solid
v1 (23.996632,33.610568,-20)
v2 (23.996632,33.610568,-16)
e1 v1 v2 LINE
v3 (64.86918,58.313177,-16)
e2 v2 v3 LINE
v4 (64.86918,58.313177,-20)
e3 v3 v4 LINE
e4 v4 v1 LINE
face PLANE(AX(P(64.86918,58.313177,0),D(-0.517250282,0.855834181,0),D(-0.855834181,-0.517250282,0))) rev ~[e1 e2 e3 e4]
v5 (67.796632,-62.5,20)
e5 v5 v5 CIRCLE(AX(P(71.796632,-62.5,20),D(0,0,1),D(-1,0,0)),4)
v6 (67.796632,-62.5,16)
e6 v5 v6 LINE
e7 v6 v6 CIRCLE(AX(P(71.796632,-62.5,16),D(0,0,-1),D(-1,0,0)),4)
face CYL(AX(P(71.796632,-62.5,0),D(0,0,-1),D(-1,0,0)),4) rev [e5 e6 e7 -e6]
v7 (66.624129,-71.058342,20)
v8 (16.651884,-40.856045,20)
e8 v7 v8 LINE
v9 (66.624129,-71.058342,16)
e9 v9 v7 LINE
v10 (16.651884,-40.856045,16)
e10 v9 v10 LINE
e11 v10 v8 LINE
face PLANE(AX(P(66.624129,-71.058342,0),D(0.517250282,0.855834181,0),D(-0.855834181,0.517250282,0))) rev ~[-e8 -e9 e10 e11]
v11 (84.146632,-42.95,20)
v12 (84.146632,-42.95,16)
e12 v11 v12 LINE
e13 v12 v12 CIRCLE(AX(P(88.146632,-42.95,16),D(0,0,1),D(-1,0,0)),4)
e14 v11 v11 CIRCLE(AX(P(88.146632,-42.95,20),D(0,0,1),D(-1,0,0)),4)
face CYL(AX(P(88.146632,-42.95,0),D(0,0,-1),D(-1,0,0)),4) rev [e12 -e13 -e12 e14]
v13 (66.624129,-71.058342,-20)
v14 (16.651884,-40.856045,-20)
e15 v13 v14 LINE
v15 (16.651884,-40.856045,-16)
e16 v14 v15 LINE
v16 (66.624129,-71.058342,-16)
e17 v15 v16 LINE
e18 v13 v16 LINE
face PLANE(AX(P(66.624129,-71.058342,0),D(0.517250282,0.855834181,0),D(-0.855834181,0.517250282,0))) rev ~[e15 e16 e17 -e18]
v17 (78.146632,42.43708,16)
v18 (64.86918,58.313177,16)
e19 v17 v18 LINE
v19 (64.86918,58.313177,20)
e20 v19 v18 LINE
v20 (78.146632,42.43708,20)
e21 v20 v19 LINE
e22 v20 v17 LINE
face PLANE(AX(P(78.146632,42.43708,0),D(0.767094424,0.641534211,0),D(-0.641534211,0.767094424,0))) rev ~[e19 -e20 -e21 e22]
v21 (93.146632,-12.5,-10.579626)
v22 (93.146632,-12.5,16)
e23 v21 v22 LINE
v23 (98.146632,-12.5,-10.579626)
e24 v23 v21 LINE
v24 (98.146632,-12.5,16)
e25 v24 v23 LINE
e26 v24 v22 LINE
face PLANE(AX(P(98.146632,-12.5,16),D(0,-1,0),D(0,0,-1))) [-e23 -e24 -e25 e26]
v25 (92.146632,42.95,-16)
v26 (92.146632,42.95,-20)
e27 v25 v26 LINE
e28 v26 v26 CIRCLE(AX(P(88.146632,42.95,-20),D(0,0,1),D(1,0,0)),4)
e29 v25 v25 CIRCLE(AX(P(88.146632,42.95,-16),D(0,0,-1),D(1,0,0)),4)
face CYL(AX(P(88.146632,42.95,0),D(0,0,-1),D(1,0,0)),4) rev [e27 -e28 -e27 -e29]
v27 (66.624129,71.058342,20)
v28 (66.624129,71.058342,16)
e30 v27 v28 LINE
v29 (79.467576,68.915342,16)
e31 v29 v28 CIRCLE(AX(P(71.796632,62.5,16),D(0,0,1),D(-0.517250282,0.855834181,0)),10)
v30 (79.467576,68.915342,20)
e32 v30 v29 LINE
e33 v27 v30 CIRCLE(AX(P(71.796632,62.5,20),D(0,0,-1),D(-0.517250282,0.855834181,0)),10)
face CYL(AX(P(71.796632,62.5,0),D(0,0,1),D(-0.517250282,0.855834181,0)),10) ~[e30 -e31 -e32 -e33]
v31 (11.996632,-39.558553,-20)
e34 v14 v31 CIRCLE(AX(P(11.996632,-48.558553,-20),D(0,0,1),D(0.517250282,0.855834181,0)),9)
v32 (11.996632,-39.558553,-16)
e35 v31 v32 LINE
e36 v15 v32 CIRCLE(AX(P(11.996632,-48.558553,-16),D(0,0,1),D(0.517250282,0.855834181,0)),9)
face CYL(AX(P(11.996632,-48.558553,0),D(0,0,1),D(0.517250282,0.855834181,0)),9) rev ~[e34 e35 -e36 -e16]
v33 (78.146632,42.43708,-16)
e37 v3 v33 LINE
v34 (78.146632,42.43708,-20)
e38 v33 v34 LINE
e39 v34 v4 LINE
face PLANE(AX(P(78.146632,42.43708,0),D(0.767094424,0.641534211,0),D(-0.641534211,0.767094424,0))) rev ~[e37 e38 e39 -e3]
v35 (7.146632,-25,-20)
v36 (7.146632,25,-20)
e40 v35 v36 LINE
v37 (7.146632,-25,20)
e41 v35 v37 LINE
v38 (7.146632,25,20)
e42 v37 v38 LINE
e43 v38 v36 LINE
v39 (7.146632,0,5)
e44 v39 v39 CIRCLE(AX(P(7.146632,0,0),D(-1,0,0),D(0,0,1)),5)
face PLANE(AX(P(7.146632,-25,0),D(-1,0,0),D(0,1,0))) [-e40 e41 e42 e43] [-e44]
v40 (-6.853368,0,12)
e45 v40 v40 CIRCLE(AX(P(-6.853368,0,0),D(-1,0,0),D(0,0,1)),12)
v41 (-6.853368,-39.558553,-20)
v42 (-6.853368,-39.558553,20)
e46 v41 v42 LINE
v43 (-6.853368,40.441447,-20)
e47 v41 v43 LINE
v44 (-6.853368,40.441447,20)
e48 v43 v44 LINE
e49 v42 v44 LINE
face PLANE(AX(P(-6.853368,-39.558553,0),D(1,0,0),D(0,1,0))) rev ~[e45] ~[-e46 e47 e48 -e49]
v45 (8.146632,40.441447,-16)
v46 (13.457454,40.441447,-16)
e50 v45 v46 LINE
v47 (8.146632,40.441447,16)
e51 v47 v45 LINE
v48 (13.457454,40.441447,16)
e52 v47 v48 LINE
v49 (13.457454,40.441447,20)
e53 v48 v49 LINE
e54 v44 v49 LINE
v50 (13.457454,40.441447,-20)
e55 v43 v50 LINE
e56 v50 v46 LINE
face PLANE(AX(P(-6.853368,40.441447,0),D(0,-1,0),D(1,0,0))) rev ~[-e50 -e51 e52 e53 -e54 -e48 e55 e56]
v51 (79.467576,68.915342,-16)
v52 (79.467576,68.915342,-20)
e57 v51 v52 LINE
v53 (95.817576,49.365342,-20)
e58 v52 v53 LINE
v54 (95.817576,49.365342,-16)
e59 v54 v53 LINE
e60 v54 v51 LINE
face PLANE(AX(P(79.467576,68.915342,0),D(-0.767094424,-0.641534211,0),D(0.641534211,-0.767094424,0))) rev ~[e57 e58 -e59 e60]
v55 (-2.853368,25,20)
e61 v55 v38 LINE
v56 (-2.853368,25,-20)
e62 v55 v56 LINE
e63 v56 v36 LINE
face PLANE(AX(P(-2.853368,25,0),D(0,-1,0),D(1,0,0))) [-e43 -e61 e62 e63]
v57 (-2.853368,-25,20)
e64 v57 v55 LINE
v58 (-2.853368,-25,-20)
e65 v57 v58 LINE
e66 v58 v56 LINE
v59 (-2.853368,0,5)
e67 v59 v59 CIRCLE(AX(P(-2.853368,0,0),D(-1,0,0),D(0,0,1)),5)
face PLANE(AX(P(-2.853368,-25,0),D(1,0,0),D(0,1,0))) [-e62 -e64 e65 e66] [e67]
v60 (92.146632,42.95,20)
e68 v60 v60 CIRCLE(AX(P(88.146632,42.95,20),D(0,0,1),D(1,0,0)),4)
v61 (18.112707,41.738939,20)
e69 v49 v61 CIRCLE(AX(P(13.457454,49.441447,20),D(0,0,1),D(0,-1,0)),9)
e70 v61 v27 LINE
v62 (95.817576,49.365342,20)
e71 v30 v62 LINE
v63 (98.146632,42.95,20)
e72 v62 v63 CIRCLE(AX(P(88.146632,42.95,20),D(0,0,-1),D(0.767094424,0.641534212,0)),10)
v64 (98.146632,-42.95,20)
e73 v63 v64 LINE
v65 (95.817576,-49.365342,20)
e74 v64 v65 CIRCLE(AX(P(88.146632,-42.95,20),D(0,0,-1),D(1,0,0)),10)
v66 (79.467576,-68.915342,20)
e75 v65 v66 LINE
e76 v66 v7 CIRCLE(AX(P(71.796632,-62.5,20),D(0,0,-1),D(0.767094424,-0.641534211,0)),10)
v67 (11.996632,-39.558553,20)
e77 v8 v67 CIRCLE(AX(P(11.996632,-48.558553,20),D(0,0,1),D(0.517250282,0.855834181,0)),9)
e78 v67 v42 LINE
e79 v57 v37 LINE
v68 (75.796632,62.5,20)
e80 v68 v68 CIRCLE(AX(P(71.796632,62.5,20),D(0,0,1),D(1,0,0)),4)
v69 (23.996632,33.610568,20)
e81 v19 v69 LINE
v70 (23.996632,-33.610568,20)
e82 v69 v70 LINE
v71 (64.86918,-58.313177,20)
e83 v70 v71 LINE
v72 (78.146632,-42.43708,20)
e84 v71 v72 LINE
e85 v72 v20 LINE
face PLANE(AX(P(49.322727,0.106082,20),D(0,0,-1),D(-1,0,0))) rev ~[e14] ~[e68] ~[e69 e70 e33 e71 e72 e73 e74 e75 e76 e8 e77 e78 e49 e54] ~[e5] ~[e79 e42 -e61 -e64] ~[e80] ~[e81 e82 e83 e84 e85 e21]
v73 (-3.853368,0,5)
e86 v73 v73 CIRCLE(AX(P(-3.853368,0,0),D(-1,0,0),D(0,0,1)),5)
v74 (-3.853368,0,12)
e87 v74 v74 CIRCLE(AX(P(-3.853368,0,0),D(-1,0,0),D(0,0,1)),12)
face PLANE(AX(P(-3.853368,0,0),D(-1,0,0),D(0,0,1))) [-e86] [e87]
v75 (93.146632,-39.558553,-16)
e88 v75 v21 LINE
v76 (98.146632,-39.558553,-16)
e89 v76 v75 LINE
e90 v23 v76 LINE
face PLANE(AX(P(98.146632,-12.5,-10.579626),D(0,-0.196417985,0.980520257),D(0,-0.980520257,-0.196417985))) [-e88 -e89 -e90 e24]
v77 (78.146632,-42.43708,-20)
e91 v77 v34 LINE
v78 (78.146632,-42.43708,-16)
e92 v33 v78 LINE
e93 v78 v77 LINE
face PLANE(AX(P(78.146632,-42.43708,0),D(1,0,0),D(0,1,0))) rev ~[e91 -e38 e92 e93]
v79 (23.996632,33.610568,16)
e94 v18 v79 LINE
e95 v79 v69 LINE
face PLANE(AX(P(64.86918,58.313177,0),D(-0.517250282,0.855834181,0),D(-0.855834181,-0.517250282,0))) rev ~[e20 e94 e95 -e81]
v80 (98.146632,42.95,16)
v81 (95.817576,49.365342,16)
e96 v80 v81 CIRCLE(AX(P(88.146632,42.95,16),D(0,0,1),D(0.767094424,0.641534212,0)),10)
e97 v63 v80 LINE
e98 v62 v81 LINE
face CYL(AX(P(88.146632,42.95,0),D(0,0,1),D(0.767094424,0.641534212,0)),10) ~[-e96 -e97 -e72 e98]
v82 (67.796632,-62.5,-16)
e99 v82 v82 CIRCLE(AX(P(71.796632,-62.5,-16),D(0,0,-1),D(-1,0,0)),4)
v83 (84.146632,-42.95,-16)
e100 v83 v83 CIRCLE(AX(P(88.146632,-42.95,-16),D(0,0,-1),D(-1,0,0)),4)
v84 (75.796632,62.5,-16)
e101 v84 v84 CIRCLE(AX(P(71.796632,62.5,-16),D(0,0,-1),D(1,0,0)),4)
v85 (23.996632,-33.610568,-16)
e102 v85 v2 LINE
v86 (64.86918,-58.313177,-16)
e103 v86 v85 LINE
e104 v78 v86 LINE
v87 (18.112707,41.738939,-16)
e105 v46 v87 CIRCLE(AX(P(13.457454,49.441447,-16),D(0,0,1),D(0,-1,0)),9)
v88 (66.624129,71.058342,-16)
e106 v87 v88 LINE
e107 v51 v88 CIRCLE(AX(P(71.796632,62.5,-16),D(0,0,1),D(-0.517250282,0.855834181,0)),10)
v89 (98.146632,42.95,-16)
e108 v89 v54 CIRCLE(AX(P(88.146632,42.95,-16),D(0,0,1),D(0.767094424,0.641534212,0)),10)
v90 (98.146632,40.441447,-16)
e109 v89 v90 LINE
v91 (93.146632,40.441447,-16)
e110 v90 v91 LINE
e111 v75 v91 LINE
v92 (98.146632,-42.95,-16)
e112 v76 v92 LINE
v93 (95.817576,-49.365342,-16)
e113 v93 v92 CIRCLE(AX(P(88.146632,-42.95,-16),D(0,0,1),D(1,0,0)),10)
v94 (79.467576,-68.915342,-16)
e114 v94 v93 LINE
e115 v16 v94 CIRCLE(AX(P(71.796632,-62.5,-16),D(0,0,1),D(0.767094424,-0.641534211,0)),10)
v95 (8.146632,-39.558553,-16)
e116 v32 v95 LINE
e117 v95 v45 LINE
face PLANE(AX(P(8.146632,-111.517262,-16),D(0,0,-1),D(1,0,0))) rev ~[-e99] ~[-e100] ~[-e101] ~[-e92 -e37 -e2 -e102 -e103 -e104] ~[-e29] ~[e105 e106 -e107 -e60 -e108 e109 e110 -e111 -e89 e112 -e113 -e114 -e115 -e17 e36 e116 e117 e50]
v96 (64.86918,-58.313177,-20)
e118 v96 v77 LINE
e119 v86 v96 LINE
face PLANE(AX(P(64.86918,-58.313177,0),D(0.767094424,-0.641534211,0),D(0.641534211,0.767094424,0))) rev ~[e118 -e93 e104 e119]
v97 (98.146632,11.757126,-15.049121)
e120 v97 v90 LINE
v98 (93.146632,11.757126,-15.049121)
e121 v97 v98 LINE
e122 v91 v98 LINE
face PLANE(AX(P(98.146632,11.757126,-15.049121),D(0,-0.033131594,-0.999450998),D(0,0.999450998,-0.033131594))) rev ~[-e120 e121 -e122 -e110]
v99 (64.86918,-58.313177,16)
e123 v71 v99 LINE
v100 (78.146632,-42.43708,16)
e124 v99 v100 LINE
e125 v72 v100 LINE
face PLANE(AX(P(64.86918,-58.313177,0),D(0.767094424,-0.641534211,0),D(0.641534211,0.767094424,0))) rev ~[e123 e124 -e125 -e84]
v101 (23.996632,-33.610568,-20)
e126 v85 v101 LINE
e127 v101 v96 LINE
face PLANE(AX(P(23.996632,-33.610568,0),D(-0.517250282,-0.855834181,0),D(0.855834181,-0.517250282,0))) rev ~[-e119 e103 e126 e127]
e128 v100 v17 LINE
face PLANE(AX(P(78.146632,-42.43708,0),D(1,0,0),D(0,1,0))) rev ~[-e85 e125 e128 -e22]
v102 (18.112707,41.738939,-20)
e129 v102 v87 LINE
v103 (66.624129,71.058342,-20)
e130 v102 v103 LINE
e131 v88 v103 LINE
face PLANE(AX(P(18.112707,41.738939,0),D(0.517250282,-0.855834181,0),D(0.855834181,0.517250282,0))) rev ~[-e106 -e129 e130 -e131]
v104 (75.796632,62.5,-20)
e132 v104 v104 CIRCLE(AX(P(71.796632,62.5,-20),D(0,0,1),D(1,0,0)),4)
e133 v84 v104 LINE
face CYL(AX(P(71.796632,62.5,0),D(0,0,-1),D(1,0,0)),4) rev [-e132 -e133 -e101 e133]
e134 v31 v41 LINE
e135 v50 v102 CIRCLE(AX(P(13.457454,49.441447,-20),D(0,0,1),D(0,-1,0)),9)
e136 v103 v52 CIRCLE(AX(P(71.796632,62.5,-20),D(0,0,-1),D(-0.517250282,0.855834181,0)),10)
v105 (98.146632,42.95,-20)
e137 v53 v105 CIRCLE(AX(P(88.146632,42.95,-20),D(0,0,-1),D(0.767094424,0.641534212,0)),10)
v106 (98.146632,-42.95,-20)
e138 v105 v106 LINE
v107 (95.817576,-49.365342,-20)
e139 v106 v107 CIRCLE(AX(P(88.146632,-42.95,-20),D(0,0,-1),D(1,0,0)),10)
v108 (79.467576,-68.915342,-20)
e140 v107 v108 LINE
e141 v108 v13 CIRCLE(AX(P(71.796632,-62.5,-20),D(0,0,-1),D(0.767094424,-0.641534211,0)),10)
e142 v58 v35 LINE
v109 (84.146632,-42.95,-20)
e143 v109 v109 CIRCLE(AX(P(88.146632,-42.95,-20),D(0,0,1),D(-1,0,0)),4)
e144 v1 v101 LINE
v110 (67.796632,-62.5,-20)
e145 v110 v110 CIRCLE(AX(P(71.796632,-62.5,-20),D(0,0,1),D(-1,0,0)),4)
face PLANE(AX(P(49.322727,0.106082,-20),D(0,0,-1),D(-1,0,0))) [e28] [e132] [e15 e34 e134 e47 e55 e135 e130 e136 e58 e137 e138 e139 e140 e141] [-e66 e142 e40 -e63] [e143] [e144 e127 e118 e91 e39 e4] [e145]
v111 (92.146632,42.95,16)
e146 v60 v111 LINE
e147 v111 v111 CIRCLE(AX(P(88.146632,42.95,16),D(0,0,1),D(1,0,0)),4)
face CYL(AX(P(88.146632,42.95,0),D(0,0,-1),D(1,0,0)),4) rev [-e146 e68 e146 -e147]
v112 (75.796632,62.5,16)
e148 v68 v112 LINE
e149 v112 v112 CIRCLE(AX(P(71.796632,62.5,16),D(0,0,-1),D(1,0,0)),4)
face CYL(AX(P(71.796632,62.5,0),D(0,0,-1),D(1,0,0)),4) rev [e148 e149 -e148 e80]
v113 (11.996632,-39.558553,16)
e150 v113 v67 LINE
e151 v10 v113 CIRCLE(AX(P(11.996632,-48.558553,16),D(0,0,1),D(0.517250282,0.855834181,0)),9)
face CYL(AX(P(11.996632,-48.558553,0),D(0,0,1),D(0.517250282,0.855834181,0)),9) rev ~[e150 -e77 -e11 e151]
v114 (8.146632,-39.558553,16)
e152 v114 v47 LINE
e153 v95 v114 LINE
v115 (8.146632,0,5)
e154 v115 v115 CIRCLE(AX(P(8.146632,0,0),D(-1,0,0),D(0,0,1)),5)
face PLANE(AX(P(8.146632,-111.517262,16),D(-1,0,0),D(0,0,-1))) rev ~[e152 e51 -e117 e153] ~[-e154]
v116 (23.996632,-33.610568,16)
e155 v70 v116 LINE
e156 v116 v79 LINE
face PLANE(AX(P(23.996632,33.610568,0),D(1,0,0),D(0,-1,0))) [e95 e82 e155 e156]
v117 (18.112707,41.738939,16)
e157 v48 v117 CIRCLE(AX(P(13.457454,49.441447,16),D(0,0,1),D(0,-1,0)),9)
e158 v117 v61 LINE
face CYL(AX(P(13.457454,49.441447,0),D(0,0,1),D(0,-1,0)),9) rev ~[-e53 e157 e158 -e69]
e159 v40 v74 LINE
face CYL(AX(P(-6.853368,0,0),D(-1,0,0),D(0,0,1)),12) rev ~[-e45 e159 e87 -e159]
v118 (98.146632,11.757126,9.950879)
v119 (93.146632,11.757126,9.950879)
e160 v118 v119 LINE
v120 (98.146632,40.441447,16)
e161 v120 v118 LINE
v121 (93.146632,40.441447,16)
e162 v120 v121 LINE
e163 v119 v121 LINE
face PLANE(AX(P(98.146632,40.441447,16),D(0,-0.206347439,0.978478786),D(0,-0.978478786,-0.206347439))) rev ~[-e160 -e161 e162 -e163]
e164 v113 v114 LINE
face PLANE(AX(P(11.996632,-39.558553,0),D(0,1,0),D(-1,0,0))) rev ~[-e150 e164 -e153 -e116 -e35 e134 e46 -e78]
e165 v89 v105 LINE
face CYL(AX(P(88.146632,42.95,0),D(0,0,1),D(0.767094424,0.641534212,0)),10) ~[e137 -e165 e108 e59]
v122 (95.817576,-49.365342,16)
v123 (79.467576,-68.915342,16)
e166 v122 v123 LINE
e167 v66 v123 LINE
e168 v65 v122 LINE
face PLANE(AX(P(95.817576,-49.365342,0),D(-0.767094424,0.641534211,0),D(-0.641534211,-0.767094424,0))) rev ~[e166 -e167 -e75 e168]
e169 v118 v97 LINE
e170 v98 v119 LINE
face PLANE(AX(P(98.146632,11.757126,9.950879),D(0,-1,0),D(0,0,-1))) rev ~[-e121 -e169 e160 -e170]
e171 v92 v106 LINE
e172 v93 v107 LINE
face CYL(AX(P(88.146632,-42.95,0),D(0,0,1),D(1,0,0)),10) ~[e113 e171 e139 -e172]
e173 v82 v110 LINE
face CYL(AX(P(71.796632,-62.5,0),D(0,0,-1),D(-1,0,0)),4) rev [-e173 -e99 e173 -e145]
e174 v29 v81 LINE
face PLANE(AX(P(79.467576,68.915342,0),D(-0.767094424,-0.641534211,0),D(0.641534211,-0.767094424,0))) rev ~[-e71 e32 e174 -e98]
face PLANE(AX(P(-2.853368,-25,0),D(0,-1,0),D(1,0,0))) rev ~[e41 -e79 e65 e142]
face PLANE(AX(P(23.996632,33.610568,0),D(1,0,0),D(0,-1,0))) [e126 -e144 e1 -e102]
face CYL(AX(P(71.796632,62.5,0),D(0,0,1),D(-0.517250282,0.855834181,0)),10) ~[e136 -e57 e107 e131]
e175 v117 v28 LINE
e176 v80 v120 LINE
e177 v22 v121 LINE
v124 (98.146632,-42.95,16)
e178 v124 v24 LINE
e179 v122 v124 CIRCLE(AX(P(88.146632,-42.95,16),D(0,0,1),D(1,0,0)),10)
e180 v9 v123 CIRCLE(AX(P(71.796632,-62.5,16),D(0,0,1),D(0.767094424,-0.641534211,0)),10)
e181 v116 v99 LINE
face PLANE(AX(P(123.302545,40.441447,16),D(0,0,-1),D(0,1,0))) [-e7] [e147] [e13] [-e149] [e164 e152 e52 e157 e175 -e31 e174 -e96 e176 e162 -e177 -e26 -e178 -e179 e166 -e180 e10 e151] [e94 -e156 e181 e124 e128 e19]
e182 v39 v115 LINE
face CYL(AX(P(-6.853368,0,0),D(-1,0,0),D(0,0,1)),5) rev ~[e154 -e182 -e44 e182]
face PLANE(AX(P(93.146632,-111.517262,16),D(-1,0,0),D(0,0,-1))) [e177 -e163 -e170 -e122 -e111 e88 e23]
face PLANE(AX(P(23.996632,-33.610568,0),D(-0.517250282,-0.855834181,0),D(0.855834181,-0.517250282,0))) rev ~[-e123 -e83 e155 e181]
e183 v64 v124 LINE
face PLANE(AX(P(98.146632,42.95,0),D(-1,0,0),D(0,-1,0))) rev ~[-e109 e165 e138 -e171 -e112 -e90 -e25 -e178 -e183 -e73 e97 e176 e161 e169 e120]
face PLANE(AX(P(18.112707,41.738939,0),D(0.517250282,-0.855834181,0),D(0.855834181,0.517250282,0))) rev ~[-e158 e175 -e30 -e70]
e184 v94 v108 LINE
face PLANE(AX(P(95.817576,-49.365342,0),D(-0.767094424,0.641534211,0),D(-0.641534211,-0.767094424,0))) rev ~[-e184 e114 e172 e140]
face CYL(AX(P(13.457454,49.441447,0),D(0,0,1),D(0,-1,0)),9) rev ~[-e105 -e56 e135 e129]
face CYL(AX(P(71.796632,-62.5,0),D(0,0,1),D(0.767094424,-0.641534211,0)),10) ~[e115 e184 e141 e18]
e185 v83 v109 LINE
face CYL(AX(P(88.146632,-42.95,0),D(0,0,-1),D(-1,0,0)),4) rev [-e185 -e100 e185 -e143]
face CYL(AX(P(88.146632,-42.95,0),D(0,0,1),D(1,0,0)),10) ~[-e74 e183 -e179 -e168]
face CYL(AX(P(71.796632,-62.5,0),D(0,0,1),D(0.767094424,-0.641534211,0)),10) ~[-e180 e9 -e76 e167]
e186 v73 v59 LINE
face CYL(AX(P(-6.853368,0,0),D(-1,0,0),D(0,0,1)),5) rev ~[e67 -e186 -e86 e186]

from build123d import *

# Parameters (mm, degrees)
BRACKET_PROFILE_SKETCH_R    = 4
BRACKET_PROFILE_SKETCH_W    = 10
BRACKET_PROFILE_SKETCH_H    = 50
BRACKET_BODY_DEPTH          = 20
SIDE_CUTOUT_DEPTH           = 151.958708937
SIDE_CUTOUT_DEPTH_BACK      = 151.958708937
SIDE_CUTOUT_SKETCH_W        = 85
SIDE_CUTOUT_SKETCH_H        = 32
INNER_WINDOW_CUT_DEPTH      = 130.155913531
INNER_WINDOW_CUT_DEPTH_BACK = 130.155913531
INNER_WINDOW_SKETCH_W       = 32
INNER_WINDOW_SKETCH_H       = 12.117592982
INNER_WINDOW_SKETCH_H_2     = 13.000486956
SIDE_OPENINGS_CUT_DEPTH     = 40
HOLE_10_SKETCH_R            = 5
THROUGH_HOLE_10_DEPTH       = 40
RECESS_24_SKETCH_R          = 12
RECESS_24X3_DEPTH           = 3


with BuildPart() as part:
    # Bracket Profile Sketch → Bracket Body (new, symmetric)
    with BuildSketch(Plane.XY):
        with BuildLine():
            Line((18.112706939, 41.738939357), (66.624129095, 71.058341812))
            ThreePointArc((66.624129095, 71.058341812), (73.442433942, 72.363637042), (79.467576157, 68.915342115))
            Line((79.467576157, 68.915342115), (95.817576157, 49.365342115))
            ThreePointArc((95.817576157, 49.365342115), (97.546351125, 46.362517955), (98.146631916, 42.95))
            Line((98.146631916, 42.95), (98.146631916, -42.95))
            ThreePointArc((98.146631916, -42.95), (97.546351125, -46.362517955), (95.817576157, -49.365342115))
            Line((95.817576157, -49.365342115), (79.467576157, -68.915342115))
            ThreePointArc((79.467576157, -68.915342115), (73.442433942, -72.363637042), (66.624129095, -71.058341812))
            Line((66.624129095, -71.058341812), (16.651884454, -40.856045382))
            ThreePointArc((16.651884454, -40.856045382), (14.412975364, -39.88899222), (11.996631916, -39.558553013))
            Line((11.996631916, -39.558553013), (-6.853368084, -39.558553013))
            Line((-6.853368084, -39.558553013), (-6.853368084, 40.441446987))
            Line((-6.853368084, 40.441446987), (13.4574544, 40.441446987))
            ThreePointArc((13.4574544, 40.441446987), (15.873797849, 40.771886195), (18.112706939, 41.738939357))
        make_face()
        with Locations((88.146631916, 42.95)):
            Circle(BRACKET_PROFILE_SKETCH_R, mode=Mode.SUBTRACT)
        with Locations((71.796631916, 62.5)):
            Circle(BRACKET_PROFILE_SKETCH_R, mode=Mode.SUBTRACT)
        with Locations(Location((88.146631916, -42.95, 0), (0, 0, 180))):
            Circle(BRACKET_PROFILE_SKETCH_R, mode=Mode.SUBTRACT)
        with Locations(Location((71.796631916, -62.5, 0), (0, 0, 180))):
            Circle(BRACKET_PROFILE_SKETCH_R, mode=Mode.SUBTRACT)
        with Locations((2.146631916, 0)):
            Rectangle(BRACKET_PROFILE_SKETCH_W, BRACKET_PROFILE_SKETCH_H, mode=Mode.SUBTRACT)
        Polygon((23.996631916, 33.610567881), (23.996631916, -33.610567881), (64.869180084, -58.31317679), (78.146631916, -42.437079952), (78.146631916, 42.437079952), (64.869180084, 58.31317679), align=None, mode=Mode.SUBTRACT)
    extrude(amount=BRACKET_BODY_DEPTH, both=True)

    # Side Cutout Sketch → Side Cutout (cut, two sides: drawn at the far end of the back side and taken through both)
    with BuildSketch(Plane(origin=(0, 40.441446987, 0), x_dir=(1, 0, 0), z_dir=(0, 1, 0)).offset(-SIDE_CUTOUT_DEPTH_BACK)):
        with Locations((50.646631916, 0)):
            Rectangle(SIDE_CUTOUT_SKETCH_W, SIDE_CUTOUT_SKETCH_H)
    extrude(amount=SIDE_CUTOUT_DEPTH + SIDE_CUTOUT_DEPTH_BACK, mode=Mode.SUBTRACT)

    # Inner Window Sketch → Inner Window Cut (cut, two sides: drawn at the far end of the back side and taken through both)
    with BuildSketch(Plane.ZY.offset(6.853368084).offset(-INNER_WINDOW_CUT_DEPTH_BACK)):
        with Locations((0, 46.500243478)):
            Rectangle(INNER_WINDOW_SKETCH_W, INNER_WINDOW_SKETCH_H)
        with Locations((0, -46.058796491)):
            Rectangle(INNER_WINDOW_SKETCH_W, INNER_WINDOW_SKETCH_H_2)
    extrude(amount=INNER_WINDOW_CUT_DEPTH + INNER_WINDOW_CUT_DEPTH_BACK, mode=Mode.SUBTRACT)

    # Side Openings Sketch → Side Openings Cut (cut)
    with BuildSketch(Plane(origin=(98.146631916, 0, 0), x_dir=(0, 0, -1), z_dir=(1, 0, 0))):
        Polygon((-16, -39.558553013), (-16, -12.5), (10.579626048, -12.5), (16, -39.558553013), align=None)
        Polygon((-16, 40.441446987), (-9.950879321, 11.757125531), (15.049120679, 11.757125531), (16, 40.441446987), align=None)
    extrude(amount=-SIDE_OPENINGS_CUT_DEPTH, mode=Mode.SUBTRACT)

    # Hole Ø10 Sketch → Through Hole Ø10 (cut)
    with BuildSketch(Plane.ZY.offset(6.853368084)):
        Circle(HOLE_10_SKETCH_R)
    extrude(amount=-THROUGH_HOLE_10_DEPTH, mode=Mode.SUBTRACT)

    # Recess Ø24 Sketch → Recess Ø24x3 (cut)
    with BuildSketch(Plane.ZY.offset(6.853368084)):
        Circle(RECESS_24_SKETCH_R)
    extrude(amount=-RECESS_24X3_DEPTH, mode=Mode.SUBTRACT)


solid = part.part
